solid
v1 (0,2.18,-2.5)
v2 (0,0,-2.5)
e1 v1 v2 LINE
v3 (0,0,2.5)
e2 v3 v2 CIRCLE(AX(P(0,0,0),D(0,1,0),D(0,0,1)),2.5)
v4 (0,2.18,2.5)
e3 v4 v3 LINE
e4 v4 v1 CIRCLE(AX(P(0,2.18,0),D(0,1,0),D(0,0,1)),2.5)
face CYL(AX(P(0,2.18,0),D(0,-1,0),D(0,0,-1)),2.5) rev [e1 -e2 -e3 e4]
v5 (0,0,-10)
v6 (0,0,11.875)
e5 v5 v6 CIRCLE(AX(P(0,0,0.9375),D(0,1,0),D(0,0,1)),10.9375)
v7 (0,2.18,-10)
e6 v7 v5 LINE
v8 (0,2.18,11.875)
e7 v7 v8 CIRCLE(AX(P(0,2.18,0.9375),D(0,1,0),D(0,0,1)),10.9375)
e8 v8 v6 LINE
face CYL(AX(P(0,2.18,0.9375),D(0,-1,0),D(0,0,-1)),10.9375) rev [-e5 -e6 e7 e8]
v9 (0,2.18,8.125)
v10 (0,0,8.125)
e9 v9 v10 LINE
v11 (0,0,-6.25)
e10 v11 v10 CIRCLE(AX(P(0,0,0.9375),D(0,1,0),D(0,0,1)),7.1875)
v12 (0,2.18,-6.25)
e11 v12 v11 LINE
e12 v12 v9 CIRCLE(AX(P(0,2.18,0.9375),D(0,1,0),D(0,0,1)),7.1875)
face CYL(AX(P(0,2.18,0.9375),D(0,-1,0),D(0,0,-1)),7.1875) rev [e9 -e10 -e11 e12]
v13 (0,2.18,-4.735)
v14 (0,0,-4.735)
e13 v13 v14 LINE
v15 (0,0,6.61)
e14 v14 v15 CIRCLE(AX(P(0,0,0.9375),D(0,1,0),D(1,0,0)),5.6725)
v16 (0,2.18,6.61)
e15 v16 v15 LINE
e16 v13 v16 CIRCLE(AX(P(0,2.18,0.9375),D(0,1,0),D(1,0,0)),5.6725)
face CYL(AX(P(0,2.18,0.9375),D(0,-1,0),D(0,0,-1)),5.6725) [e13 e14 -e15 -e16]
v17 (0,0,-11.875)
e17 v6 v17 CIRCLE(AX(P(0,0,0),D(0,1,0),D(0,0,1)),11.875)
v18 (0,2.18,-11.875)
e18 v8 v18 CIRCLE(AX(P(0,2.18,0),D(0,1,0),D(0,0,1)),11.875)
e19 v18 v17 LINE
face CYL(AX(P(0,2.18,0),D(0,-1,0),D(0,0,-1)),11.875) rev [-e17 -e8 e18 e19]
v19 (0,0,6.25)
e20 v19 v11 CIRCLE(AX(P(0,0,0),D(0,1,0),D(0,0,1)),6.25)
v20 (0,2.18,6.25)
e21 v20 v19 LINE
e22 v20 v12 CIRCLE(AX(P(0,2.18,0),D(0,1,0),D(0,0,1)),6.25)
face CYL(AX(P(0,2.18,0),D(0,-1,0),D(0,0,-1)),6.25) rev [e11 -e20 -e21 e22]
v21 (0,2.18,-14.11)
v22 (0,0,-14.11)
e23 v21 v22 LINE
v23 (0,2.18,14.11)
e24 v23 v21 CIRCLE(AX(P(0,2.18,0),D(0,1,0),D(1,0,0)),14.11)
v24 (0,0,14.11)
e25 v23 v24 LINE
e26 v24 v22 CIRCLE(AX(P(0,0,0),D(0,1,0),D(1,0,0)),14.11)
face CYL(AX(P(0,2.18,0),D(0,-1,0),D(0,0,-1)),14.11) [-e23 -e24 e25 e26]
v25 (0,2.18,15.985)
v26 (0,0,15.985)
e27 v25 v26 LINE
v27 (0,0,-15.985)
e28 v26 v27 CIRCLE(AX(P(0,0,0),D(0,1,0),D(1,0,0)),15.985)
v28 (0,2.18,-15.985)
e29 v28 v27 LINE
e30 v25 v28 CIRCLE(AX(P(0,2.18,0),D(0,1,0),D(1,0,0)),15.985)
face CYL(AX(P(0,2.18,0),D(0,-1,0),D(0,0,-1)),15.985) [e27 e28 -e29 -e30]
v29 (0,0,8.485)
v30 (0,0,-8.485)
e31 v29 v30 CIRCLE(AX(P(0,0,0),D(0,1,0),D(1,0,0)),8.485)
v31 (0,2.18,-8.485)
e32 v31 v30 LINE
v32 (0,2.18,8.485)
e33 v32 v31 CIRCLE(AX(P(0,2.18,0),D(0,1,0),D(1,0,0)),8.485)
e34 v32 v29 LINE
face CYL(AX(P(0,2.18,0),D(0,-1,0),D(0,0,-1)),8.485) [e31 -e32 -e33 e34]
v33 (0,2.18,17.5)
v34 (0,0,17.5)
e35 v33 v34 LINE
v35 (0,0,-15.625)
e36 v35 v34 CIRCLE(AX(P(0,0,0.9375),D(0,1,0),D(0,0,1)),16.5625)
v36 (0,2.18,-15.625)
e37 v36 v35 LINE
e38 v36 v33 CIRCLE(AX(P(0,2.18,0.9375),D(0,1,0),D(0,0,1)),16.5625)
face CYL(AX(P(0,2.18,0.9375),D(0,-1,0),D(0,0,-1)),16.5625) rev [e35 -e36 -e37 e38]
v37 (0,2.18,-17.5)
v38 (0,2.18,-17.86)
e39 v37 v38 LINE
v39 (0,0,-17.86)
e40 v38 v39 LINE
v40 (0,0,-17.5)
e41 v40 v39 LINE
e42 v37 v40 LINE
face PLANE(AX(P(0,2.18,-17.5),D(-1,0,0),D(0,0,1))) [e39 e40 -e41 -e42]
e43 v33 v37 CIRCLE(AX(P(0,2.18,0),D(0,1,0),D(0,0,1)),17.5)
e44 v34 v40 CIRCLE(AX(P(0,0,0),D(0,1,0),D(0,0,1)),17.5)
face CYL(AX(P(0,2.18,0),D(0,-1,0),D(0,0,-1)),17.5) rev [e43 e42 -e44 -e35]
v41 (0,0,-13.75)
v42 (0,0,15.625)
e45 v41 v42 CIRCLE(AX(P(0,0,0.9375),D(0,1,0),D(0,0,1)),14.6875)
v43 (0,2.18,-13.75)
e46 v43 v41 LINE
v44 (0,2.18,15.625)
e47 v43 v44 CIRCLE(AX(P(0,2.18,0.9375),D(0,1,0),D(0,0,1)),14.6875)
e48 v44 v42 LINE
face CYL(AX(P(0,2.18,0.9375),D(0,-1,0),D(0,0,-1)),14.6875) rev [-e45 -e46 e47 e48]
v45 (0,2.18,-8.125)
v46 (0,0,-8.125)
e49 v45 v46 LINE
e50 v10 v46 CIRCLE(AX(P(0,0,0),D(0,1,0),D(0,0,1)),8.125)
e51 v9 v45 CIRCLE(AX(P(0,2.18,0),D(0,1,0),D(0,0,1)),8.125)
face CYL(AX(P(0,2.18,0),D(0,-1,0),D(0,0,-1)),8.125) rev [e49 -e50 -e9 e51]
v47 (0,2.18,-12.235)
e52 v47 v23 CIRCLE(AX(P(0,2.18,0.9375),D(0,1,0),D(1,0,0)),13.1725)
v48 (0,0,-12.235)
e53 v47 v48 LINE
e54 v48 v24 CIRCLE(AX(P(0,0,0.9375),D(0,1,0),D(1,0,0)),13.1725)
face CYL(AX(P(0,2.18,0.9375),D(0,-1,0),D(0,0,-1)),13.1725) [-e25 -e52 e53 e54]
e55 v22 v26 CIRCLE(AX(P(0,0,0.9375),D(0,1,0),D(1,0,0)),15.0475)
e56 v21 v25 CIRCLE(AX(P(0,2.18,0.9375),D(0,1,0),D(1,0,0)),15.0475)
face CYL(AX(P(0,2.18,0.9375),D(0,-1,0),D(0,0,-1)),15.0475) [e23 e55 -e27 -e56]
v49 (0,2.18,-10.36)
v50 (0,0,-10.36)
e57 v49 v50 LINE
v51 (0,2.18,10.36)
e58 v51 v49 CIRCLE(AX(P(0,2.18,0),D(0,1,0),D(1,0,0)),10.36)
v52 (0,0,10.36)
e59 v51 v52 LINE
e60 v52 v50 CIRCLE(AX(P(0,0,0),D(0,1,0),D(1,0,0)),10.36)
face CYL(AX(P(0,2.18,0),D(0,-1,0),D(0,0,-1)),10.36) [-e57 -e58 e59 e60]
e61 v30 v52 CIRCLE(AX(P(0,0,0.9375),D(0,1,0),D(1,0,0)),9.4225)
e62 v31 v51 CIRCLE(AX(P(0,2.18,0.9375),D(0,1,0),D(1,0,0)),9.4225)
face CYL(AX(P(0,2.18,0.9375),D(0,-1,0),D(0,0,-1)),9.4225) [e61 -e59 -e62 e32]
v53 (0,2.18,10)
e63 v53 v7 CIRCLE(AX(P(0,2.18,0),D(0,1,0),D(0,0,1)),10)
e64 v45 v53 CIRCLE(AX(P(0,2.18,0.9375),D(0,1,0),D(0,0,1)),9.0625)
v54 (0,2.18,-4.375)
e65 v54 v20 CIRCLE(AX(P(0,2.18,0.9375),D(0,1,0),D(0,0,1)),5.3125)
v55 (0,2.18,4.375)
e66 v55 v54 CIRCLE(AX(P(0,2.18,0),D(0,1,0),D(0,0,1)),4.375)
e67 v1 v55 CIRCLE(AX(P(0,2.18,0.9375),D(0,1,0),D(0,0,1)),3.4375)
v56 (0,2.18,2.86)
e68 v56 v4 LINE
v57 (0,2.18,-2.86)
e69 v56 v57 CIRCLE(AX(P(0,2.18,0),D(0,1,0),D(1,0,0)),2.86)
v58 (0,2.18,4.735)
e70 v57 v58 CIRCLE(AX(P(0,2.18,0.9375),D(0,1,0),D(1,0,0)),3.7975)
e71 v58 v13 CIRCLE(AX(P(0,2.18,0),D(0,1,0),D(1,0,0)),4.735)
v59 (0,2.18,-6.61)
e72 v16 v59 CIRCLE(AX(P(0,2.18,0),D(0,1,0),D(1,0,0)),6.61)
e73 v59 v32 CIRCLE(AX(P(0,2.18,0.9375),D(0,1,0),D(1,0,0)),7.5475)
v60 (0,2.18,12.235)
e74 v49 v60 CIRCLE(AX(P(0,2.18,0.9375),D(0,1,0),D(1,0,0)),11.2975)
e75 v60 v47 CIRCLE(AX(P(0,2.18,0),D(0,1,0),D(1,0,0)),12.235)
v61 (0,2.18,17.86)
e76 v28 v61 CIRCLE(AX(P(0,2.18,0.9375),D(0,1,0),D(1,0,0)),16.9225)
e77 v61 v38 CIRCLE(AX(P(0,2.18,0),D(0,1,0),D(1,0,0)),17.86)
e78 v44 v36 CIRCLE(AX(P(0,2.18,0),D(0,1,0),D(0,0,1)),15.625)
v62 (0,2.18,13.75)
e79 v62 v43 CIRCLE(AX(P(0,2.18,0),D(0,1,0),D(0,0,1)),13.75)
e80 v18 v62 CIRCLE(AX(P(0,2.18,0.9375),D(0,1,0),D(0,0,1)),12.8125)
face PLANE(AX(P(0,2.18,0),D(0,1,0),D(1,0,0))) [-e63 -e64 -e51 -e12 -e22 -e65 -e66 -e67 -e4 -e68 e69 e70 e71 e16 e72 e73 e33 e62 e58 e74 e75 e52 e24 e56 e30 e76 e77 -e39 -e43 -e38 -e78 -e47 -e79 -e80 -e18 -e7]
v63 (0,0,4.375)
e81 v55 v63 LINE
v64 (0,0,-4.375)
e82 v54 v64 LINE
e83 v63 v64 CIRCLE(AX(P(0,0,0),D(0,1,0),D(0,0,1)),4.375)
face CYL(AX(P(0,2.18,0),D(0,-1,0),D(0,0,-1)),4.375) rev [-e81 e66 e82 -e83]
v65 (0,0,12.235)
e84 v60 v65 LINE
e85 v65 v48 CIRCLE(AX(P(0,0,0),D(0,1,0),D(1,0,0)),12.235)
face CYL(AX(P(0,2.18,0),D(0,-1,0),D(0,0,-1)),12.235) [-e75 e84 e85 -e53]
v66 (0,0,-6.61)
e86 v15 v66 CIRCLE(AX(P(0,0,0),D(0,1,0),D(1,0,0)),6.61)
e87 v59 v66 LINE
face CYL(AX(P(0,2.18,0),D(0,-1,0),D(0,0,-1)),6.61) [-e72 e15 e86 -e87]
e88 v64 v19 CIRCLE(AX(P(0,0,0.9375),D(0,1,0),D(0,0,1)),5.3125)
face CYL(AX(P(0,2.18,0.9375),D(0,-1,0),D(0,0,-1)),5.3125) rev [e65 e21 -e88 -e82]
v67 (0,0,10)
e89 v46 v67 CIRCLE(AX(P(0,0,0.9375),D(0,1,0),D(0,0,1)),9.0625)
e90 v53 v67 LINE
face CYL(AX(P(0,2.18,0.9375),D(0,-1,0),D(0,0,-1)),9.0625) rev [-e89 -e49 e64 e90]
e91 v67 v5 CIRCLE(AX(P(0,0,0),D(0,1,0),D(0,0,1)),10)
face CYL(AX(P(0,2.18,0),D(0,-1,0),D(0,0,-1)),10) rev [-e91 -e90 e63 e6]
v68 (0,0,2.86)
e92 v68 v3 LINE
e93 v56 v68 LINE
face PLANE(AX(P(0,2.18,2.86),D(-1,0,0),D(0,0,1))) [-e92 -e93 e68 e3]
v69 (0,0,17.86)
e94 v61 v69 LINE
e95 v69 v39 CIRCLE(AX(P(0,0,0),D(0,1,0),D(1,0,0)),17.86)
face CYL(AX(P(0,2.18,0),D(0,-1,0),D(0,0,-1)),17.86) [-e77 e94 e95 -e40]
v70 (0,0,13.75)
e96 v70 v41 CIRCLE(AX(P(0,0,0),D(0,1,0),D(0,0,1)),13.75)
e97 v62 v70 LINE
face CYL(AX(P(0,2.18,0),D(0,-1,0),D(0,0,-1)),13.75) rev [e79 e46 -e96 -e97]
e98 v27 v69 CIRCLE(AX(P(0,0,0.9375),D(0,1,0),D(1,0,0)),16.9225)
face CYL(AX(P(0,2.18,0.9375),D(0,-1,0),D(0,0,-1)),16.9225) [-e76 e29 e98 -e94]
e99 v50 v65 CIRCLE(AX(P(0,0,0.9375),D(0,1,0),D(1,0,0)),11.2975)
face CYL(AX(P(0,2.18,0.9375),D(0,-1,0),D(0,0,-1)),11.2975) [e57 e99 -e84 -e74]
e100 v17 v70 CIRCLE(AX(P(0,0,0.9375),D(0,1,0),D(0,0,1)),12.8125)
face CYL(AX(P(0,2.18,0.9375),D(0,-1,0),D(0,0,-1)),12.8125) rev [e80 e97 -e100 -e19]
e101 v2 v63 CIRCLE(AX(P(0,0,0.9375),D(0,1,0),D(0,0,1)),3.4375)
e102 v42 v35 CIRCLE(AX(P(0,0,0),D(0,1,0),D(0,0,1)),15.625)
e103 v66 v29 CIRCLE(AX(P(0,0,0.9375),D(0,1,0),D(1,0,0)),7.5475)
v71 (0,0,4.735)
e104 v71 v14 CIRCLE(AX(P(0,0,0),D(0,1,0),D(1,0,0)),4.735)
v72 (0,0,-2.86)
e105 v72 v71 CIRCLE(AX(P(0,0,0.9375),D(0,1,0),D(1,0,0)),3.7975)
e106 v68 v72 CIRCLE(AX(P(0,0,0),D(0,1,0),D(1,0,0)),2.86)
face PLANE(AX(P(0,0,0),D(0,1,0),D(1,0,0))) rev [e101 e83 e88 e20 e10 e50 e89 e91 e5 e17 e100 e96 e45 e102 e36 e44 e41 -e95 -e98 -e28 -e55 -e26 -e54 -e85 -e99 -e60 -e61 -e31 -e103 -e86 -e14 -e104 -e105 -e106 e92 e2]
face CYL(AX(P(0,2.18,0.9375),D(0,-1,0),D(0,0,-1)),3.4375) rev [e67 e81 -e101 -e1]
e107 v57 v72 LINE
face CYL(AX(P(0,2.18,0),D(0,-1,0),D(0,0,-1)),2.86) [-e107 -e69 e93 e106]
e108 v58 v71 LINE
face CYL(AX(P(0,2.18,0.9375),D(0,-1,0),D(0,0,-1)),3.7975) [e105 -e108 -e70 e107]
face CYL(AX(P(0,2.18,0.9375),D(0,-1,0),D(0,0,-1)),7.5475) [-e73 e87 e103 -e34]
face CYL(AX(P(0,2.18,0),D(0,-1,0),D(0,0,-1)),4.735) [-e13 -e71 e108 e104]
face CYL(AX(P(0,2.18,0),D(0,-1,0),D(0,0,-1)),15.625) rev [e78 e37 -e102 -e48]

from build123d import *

# Parameters (mm, degrees)
EXTRUDE_THIN_2_DEPTH = 2.18


with BuildPart() as part:
    # Sketch 1 → Extrude-thin 2 (new body)
    with BuildSketch(Plane(origin=(0, 0, 0), x_dir=(1, 0, 0), z_dir=(0, 1, 0))):
        with BuildLine():
            ThreePointArc((0, -2.5), (2.5, 0), (0, 2.5))
            ThreePointArc((0, 2.5), (-3.4375, -0.9375), (0, -4.375))
            ThreePointArc((0, -4.375), (4.375, 0), (0, 4.375))
            ThreePointArc((0, 4.375), (-5.3125, -0.9375), (0, -6.25))
            ThreePointArc((0, -6.25), (6.25, 0), (0, 6.25))
            ThreePointArc((0, 6.25), (-7.1875, -0.9375), (0, -8.125))
            ThreePointArc((0, -8.125), (8.125, 0), (0, 8.125))
            ThreePointArc((0, 8.125), (-9.0625, -0.9375), (0, -10))
            ThreePointArc((0, -10), (10, 0), (0, 10))
            ThreePointArc((0, 10), (-10.9375, -0.9375), (0, -11.875))
            ThreePointArc((0, -11.875), (11.875, 0), (0, 11.875))
            ThreePointArc((0, 11.875), (-12.8125, -0.9375), (0, -13.75))
            ThreePointArc((0, -13.75), (13.75, 0), (0, 13.75))
            ThreePointArc((0, 13.75), (-14.6875, -0.9375), (0, -15.625))
            ThreePointArc((0, -15.625), (15.625, 0), (0, 15.625))
            ThreePointArc((0, 15.625), (-16.5625, -0.9375), (0, -17.5))
            ThreePointArc((0, -17.5), (17.5, 0), (0, 17.5))
            Line((0, 17.5), (0, 17.86))
            ThreePointArc((0, 17.86), (17.86, 0), (0, -17.86))
            ThreePointArc((0, -17.86), (-16.9225, -0.9375), (0, 15.985))
            ThreePointArc((0, 15.985), (15.985, 0), (0, -15.985))
            ThreePointArc((0, -15.985), (-15.0475, -0.9375), (0, 14.11))
            ThreePointArc((0, 14.11), (14.11, 0), (0, -14.11))
            ThreePointArc((0, -14.11), (-13.1725, -0.9375), (0, 12.235))
            ThreePointArc((0, 12.235), (12.235, 0), (0, -12.235))
            ThreePointArc((0, -12.235), (-11.2975, -0.9375), (0, 10.36))
            ThreePointArc((0, 10.36), (10.36, 0), (0, -10.36))
            ThreePointArc((0, -10.36), (-9.4225, -0.9375), (0, 8.485))
            ThreePointArc((0, 8.485), (8.485, 0), (0, -8.485))
            ThreePointArc((0, -8.485), (-7.5475, -0.9375), (0, 6.61))
            ThreePointArc((0, 6.61), (6.61, 0), (0, -6.61))
            ThreePointArc((0, -6.61), (-5.6725, -0.9375), (0, 4.735))
            ThreePointArc((0, 4.735), (4.735, 0), (0, -4.735))
            ThreePointArc((0, -4.735), (-3.7975, -0.9375), (0, 2.86))
            ThreePointArc((0, 2.86), (2.86, 0), (0, -2.86))
            Line((0, -2.86), (0, -2.5))
        make_face()
    extrude(amount=EXTRUDE_THIN_2_DEPTH)


solid = part.part
